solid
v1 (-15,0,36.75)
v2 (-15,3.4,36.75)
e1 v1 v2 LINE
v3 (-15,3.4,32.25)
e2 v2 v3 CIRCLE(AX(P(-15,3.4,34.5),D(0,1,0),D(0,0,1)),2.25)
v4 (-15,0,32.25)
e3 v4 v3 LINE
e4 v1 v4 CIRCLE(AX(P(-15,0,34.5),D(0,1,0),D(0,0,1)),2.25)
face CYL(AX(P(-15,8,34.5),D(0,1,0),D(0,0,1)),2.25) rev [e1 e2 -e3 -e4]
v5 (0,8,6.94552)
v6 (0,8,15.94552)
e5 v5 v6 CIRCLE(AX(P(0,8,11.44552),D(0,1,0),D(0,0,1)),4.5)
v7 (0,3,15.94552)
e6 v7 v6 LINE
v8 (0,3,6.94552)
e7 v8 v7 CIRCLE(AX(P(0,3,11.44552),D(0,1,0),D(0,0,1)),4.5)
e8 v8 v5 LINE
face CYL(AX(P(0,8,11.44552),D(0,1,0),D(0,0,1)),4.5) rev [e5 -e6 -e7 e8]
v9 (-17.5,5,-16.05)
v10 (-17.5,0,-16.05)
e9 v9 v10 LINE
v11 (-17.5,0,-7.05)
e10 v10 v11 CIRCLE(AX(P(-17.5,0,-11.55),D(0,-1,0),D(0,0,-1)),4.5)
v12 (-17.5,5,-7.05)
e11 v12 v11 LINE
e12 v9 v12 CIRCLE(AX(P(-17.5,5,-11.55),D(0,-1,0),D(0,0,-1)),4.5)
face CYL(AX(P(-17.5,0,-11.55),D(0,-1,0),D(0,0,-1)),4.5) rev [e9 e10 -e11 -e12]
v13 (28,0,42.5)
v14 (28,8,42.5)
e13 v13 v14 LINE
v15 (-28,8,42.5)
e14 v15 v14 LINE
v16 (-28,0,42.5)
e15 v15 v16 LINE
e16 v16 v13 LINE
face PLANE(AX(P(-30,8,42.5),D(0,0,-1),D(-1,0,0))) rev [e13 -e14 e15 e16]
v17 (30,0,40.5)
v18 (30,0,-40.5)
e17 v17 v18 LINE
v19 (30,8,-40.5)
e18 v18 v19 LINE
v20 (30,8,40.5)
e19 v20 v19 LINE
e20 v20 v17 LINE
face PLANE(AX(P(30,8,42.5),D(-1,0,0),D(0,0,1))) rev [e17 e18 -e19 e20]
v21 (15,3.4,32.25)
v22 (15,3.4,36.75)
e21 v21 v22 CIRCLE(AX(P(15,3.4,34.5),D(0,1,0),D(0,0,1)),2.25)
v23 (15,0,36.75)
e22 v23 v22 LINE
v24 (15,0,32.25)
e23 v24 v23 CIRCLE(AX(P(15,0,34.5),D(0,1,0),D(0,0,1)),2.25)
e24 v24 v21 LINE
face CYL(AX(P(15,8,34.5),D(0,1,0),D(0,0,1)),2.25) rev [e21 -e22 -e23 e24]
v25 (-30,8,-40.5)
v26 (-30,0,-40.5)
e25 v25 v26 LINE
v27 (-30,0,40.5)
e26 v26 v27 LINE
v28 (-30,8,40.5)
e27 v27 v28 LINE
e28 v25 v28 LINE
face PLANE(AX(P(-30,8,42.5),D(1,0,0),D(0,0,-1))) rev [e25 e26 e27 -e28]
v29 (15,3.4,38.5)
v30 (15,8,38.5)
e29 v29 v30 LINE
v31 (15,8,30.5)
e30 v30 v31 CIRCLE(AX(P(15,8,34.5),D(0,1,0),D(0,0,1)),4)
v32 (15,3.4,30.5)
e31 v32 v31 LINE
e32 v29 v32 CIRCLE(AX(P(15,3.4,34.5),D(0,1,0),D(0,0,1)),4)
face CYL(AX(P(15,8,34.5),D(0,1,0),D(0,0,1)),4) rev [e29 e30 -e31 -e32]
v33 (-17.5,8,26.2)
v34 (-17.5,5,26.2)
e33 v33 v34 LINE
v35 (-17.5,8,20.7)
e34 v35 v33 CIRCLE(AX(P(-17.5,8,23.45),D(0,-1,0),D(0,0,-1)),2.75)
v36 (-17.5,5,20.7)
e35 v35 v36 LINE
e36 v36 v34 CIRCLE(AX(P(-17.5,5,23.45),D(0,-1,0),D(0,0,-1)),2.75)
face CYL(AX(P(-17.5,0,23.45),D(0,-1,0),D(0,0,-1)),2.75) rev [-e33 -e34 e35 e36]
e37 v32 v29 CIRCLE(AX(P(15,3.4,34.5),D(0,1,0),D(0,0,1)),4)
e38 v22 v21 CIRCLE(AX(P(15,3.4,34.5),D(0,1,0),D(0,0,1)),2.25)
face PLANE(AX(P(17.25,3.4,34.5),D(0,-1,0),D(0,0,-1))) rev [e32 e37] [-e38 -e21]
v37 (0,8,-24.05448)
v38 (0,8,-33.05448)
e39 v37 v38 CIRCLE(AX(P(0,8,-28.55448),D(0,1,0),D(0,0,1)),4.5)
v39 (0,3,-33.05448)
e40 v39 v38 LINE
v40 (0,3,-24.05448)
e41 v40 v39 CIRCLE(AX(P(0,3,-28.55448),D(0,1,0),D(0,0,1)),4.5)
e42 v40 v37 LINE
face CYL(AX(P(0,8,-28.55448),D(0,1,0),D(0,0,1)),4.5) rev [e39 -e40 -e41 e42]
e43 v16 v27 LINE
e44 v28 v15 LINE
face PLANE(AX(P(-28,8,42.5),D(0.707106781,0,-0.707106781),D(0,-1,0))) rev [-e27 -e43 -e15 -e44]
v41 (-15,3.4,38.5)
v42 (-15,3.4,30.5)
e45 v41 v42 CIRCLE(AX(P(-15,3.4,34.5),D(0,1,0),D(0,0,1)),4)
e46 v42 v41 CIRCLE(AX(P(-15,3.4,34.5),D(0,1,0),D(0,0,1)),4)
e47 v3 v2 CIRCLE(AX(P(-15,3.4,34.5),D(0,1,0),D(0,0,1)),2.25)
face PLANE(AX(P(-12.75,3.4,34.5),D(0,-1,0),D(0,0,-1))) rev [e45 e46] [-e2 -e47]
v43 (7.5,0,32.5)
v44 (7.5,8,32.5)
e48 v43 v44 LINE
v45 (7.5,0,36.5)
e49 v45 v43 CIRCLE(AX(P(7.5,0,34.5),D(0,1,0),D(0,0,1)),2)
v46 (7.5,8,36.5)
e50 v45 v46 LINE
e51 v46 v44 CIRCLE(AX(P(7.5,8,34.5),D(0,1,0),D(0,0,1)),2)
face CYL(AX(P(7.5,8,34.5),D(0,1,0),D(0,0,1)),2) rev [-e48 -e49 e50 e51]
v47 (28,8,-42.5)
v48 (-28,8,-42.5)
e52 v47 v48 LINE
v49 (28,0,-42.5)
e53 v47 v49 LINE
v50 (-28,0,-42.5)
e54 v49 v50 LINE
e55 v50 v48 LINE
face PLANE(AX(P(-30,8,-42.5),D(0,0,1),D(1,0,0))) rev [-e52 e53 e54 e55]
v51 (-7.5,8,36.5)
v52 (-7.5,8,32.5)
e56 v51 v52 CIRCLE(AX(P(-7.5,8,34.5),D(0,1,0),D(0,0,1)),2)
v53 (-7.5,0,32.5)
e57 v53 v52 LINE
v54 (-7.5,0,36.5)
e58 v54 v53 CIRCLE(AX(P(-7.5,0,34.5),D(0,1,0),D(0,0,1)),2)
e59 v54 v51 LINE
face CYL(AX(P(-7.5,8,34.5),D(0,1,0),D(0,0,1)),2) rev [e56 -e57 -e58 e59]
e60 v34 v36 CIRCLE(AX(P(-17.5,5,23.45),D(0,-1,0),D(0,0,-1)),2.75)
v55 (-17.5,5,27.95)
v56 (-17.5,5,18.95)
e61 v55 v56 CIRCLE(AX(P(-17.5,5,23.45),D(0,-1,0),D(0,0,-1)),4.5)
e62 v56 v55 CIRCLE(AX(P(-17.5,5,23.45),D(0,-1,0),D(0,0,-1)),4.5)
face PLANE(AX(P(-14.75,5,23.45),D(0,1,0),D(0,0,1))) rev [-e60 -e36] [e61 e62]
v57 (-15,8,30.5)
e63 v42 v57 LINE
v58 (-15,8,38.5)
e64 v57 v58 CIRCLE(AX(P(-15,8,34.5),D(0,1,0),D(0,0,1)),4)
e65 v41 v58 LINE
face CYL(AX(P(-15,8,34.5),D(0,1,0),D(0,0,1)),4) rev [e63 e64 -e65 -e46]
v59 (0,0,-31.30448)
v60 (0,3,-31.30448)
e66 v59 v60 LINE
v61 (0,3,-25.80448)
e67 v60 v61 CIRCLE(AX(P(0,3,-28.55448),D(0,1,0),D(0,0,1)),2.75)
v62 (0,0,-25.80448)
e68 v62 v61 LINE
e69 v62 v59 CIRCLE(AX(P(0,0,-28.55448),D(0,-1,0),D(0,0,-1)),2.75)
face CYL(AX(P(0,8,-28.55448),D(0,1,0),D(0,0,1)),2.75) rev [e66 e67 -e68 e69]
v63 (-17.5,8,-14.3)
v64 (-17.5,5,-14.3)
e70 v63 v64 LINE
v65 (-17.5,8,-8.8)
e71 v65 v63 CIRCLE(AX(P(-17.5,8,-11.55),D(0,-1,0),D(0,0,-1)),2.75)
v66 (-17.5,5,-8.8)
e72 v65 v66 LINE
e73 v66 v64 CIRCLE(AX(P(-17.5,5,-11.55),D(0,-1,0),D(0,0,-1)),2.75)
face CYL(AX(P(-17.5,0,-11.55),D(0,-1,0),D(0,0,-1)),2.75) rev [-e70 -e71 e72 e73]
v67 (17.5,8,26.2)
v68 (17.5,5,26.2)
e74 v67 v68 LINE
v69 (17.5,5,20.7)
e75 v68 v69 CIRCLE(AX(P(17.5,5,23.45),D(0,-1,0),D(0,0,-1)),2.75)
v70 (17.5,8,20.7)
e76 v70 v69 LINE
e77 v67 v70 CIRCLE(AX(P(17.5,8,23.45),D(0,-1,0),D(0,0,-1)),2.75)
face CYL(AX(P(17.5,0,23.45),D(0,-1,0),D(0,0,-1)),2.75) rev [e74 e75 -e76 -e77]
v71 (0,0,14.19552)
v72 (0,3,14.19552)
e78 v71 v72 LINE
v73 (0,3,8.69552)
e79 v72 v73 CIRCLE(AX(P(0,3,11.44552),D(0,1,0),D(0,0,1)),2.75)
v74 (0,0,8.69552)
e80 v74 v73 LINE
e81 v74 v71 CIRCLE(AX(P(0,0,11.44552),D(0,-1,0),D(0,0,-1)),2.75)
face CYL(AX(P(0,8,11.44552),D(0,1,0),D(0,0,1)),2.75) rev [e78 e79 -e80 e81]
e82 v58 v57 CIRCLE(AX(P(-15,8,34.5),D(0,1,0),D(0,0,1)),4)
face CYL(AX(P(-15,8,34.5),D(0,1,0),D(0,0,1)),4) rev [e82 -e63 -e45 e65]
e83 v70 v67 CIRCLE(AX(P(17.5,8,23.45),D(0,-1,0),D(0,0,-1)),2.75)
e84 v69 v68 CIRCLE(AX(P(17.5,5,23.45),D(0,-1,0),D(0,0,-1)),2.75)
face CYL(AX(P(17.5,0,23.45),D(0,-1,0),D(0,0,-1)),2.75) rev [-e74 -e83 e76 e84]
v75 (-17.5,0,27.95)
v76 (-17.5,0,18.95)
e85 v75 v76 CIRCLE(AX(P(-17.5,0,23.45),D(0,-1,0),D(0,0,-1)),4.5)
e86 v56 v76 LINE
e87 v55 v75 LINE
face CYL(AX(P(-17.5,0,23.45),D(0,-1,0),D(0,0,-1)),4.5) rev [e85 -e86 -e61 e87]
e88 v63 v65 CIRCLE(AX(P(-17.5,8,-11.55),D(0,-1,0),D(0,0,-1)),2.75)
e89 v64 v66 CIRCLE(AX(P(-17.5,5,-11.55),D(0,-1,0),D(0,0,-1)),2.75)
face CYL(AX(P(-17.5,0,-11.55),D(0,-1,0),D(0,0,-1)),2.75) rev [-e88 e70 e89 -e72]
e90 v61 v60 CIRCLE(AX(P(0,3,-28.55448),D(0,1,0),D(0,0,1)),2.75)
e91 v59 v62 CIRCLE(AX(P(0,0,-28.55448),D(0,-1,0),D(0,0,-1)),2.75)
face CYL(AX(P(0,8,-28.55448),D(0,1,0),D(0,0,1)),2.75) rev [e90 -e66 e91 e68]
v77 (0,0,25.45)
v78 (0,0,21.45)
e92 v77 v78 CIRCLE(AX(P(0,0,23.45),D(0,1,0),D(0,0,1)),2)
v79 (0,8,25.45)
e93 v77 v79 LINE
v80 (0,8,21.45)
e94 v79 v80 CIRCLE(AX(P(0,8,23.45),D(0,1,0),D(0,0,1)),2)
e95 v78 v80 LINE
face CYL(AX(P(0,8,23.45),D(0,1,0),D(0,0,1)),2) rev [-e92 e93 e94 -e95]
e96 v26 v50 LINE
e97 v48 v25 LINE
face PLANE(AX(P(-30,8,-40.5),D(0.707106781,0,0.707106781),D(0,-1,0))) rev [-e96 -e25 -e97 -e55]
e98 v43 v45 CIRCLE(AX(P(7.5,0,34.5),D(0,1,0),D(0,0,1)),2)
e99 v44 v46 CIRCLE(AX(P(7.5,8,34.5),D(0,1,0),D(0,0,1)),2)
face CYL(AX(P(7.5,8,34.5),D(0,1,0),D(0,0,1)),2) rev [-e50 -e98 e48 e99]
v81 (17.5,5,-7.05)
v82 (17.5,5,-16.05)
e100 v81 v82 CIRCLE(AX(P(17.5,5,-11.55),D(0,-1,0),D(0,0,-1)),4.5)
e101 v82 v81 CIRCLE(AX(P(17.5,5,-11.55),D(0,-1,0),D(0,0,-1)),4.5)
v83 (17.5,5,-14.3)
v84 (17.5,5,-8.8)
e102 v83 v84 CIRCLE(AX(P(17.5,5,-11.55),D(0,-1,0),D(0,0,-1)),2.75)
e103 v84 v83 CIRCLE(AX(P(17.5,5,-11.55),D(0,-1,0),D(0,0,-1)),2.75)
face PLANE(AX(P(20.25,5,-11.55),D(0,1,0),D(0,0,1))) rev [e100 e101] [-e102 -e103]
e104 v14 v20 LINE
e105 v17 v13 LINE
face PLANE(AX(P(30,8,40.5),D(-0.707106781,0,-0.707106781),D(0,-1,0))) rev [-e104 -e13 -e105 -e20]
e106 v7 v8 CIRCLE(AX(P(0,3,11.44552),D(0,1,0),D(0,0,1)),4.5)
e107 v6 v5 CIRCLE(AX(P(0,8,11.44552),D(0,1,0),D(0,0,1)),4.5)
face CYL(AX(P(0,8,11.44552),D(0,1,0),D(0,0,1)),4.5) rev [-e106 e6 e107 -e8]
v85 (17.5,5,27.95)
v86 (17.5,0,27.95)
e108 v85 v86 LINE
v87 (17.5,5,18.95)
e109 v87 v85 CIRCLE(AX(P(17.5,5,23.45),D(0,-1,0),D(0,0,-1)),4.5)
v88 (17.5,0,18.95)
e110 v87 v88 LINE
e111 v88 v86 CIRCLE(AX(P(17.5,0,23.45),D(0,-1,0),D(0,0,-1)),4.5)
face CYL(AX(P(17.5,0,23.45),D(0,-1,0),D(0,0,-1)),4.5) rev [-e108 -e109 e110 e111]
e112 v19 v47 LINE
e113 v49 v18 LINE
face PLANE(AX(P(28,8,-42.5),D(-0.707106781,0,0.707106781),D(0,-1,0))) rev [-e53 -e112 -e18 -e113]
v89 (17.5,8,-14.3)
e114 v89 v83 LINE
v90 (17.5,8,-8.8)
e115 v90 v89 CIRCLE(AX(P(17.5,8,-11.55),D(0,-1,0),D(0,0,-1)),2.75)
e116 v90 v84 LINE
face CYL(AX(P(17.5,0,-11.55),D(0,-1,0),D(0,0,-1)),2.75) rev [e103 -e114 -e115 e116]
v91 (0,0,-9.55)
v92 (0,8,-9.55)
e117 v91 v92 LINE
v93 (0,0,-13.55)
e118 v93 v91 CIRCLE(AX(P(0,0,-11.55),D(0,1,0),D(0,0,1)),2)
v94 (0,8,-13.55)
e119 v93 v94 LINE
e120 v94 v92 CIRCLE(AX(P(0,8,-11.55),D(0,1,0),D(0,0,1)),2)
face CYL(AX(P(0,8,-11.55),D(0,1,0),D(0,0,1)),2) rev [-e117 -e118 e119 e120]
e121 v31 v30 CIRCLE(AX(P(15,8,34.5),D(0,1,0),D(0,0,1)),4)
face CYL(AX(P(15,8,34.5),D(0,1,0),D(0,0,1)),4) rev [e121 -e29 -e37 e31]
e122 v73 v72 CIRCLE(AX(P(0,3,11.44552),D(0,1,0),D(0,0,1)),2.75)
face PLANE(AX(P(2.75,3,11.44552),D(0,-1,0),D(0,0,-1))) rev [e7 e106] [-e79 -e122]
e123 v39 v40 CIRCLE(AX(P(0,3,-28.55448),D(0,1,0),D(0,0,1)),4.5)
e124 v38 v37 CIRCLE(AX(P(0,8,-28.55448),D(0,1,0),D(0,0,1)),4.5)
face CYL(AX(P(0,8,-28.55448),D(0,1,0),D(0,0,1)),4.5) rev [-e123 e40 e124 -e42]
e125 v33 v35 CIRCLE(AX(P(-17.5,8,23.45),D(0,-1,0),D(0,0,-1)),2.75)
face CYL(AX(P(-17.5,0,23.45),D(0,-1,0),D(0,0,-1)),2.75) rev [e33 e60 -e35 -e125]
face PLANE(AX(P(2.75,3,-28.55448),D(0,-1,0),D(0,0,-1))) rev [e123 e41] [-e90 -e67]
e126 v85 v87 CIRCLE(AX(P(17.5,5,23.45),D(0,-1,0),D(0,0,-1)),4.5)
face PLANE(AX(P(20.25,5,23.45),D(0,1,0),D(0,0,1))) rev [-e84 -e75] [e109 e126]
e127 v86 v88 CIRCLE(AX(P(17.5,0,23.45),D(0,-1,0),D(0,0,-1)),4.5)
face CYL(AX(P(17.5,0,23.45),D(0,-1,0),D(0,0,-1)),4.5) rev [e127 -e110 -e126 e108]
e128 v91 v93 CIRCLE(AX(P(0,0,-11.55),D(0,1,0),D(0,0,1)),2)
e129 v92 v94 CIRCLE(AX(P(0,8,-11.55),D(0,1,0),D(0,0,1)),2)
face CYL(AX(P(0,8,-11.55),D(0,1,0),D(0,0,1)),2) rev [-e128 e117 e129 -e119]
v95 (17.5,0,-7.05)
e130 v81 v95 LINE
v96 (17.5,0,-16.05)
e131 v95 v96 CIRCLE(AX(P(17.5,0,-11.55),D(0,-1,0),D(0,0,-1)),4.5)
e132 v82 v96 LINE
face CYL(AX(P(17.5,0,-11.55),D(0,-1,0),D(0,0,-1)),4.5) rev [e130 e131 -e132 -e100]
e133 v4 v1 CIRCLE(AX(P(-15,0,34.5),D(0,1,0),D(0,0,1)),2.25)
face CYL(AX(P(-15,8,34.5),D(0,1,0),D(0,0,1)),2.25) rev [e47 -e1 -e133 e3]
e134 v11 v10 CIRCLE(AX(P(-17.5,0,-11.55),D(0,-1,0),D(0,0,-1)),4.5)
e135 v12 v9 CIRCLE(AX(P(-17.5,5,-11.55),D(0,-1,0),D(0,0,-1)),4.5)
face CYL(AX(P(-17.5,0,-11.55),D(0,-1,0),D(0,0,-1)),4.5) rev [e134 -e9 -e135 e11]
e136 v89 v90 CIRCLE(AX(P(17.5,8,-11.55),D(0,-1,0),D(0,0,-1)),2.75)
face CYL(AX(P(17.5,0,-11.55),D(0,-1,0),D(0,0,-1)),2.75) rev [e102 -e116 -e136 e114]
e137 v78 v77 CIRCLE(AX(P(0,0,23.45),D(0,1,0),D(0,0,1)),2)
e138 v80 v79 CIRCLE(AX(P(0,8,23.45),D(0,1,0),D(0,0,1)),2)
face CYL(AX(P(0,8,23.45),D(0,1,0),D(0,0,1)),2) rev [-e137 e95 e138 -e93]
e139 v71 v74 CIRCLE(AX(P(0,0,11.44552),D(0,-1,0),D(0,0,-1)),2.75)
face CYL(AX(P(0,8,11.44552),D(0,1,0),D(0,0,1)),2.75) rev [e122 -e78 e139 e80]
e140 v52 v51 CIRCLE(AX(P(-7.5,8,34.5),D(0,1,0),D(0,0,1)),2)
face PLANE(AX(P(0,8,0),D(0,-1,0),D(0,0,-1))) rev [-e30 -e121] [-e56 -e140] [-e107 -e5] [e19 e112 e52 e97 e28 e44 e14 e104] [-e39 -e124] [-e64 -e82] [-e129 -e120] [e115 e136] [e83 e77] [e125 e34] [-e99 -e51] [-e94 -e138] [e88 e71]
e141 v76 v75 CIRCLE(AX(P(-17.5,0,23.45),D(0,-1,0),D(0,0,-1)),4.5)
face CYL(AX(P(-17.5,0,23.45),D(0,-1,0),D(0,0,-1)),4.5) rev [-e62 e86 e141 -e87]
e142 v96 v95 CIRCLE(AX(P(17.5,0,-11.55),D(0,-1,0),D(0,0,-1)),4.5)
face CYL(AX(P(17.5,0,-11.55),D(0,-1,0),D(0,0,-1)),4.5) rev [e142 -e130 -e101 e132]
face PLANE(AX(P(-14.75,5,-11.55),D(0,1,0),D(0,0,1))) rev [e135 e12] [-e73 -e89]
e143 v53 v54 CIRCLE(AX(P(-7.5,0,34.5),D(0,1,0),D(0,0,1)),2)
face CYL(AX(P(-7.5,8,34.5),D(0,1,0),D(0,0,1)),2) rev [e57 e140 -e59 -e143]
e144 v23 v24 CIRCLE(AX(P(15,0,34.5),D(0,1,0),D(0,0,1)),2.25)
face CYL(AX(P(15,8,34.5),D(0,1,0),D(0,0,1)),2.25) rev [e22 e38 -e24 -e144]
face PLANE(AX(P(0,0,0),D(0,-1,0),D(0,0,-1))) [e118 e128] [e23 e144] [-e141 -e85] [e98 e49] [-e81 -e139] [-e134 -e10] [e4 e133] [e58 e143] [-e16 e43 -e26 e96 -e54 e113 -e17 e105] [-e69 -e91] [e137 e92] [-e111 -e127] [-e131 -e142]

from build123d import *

# Parameters (mm, degrees)
SKETCH_1_W                  = 60
SKETCH_1_H                  = 85
EXTRUDE_1_DEPTH             = 8
HOLE_WIZARD_1_D             = 5.5
HOLE_WIZARD_1_CBORE_D       = 9
HOLE_WIZARD_1_CBORE_DEPTH   = 5
HOLE_WIZARD_2_D             = 5.5
HOLE_WIZARD_2_DEPTH         = 12.4
HOLE_WIZARD_2_CBORE_D       = 9
HOLE_WIZARD_2_CBORE_DEPTH   = 5
HOLE_WIZARD_2_TIP           = 1.652366702
HOLE_WIZARD_1_2_D           = 4.5
HOLE_WIZARD_1_2_CBORE_D     = 8
HOLE_WIZARD_1_2_CBORE_DEPTH = 4.6
HOLE_WIZARD_4_0_4_1_D       = 4
CHAMFER_1_SIZE              = 2


with BuildPart() as part:
    # 草图1 → 凸台-拉伸1 (new body)
    with BuildSketch(Plane(origin=(0, 0, 0), x_dir=(1, 0, 0), z_dir=(0, 1, 0))):
        Rectangle(SKETCH_1_W, SKETCH_1_H)
    extrude(amount=EXTRUDE_1_DEPTH)

    # Hole Wizard 1 (through all)
    with Locations(Plane(origin=(0, 0, 0), x_dir=(-1, 0, 0), z_dir=(0, -1, 0))):
        with Locations((17.5, -23.45), (-17.5, -23.45), (17.5, 11.55), (-17.5, 11.55)):
            CounterBoreHole(HOLE_WIZARD_1_D / 2, HOLE_WIZARD_1_CBORE_D / 2, HOLE_WIZARD_1_CBORE_DEPTH)

    # 大小六角凹头盖螺钉柱孔2
    with Locations(Plane(origin=(0, 8, 0), x_dir=(1, 0, 0), z_dir=(0, 1, 0))):
        with Locations((0, 28.554479799), (0, -11.445520201)):
            CounterBoreHole(HOLE_WIZARD_2_D / 2, HOLE_WIZARD_2_CBORE_D / 2, HOLE_WIZARD_2_CBORE_DEPTH, depth=HOLE_WIZARD_2_DEPTH)
            with Locations((0, 0, -(HOLE_WIZARD_2_DEPTH + HOLE_WIZARD_2_TIP / 2))):  # 118° drill point
                Cone(0, HOLE_WIZARD_2_D / 2, HOLE_WIZARD_2_TIP, mode=Mode.SUBTRACT)

    # Hole Wizard 1 2 (through all)
    with Locations(Plane(origin=(0, 8, 0), x_dir=(1, 0, 0), z_dir=(0, 1, 0))):
        with Locations((-15, -34.5), (15, -34.5)):
            CounterBoreHole(HOLE_WIZARD_1_2_D / 2, HOLE_WIZARD_1_2_CBORE_D / 2, HOLE_WIZARD_1_2_CBORE_DEPTH)

    # Ø4.0 (4) 直径孔1 (through all)
    with Locations(Plane(origin=(0, 8, 0), x_dir=(1, 0, 0), z_dir=(0, 1, 0))):
        with Locations((-7.5, -34.5), (7.5, -34.5), (0, -23.45), (0, 11.55)):
            Hole(HOLE_WIZARD_4_0_4_1_D / 2)

    # 倒角1
    chamfer_1_edges = [part.edges().sort_by_distance(p)[0] for p in [
        (30, 4, 42.5),
        (-30, 4, 42.5),
        (-30, 4, -42.5),
        (30, 4, -42.5),
    ]]
    chamfer(chamfer_1_edges, length=CHAMFER_1_SIZE)


solid = part.part
